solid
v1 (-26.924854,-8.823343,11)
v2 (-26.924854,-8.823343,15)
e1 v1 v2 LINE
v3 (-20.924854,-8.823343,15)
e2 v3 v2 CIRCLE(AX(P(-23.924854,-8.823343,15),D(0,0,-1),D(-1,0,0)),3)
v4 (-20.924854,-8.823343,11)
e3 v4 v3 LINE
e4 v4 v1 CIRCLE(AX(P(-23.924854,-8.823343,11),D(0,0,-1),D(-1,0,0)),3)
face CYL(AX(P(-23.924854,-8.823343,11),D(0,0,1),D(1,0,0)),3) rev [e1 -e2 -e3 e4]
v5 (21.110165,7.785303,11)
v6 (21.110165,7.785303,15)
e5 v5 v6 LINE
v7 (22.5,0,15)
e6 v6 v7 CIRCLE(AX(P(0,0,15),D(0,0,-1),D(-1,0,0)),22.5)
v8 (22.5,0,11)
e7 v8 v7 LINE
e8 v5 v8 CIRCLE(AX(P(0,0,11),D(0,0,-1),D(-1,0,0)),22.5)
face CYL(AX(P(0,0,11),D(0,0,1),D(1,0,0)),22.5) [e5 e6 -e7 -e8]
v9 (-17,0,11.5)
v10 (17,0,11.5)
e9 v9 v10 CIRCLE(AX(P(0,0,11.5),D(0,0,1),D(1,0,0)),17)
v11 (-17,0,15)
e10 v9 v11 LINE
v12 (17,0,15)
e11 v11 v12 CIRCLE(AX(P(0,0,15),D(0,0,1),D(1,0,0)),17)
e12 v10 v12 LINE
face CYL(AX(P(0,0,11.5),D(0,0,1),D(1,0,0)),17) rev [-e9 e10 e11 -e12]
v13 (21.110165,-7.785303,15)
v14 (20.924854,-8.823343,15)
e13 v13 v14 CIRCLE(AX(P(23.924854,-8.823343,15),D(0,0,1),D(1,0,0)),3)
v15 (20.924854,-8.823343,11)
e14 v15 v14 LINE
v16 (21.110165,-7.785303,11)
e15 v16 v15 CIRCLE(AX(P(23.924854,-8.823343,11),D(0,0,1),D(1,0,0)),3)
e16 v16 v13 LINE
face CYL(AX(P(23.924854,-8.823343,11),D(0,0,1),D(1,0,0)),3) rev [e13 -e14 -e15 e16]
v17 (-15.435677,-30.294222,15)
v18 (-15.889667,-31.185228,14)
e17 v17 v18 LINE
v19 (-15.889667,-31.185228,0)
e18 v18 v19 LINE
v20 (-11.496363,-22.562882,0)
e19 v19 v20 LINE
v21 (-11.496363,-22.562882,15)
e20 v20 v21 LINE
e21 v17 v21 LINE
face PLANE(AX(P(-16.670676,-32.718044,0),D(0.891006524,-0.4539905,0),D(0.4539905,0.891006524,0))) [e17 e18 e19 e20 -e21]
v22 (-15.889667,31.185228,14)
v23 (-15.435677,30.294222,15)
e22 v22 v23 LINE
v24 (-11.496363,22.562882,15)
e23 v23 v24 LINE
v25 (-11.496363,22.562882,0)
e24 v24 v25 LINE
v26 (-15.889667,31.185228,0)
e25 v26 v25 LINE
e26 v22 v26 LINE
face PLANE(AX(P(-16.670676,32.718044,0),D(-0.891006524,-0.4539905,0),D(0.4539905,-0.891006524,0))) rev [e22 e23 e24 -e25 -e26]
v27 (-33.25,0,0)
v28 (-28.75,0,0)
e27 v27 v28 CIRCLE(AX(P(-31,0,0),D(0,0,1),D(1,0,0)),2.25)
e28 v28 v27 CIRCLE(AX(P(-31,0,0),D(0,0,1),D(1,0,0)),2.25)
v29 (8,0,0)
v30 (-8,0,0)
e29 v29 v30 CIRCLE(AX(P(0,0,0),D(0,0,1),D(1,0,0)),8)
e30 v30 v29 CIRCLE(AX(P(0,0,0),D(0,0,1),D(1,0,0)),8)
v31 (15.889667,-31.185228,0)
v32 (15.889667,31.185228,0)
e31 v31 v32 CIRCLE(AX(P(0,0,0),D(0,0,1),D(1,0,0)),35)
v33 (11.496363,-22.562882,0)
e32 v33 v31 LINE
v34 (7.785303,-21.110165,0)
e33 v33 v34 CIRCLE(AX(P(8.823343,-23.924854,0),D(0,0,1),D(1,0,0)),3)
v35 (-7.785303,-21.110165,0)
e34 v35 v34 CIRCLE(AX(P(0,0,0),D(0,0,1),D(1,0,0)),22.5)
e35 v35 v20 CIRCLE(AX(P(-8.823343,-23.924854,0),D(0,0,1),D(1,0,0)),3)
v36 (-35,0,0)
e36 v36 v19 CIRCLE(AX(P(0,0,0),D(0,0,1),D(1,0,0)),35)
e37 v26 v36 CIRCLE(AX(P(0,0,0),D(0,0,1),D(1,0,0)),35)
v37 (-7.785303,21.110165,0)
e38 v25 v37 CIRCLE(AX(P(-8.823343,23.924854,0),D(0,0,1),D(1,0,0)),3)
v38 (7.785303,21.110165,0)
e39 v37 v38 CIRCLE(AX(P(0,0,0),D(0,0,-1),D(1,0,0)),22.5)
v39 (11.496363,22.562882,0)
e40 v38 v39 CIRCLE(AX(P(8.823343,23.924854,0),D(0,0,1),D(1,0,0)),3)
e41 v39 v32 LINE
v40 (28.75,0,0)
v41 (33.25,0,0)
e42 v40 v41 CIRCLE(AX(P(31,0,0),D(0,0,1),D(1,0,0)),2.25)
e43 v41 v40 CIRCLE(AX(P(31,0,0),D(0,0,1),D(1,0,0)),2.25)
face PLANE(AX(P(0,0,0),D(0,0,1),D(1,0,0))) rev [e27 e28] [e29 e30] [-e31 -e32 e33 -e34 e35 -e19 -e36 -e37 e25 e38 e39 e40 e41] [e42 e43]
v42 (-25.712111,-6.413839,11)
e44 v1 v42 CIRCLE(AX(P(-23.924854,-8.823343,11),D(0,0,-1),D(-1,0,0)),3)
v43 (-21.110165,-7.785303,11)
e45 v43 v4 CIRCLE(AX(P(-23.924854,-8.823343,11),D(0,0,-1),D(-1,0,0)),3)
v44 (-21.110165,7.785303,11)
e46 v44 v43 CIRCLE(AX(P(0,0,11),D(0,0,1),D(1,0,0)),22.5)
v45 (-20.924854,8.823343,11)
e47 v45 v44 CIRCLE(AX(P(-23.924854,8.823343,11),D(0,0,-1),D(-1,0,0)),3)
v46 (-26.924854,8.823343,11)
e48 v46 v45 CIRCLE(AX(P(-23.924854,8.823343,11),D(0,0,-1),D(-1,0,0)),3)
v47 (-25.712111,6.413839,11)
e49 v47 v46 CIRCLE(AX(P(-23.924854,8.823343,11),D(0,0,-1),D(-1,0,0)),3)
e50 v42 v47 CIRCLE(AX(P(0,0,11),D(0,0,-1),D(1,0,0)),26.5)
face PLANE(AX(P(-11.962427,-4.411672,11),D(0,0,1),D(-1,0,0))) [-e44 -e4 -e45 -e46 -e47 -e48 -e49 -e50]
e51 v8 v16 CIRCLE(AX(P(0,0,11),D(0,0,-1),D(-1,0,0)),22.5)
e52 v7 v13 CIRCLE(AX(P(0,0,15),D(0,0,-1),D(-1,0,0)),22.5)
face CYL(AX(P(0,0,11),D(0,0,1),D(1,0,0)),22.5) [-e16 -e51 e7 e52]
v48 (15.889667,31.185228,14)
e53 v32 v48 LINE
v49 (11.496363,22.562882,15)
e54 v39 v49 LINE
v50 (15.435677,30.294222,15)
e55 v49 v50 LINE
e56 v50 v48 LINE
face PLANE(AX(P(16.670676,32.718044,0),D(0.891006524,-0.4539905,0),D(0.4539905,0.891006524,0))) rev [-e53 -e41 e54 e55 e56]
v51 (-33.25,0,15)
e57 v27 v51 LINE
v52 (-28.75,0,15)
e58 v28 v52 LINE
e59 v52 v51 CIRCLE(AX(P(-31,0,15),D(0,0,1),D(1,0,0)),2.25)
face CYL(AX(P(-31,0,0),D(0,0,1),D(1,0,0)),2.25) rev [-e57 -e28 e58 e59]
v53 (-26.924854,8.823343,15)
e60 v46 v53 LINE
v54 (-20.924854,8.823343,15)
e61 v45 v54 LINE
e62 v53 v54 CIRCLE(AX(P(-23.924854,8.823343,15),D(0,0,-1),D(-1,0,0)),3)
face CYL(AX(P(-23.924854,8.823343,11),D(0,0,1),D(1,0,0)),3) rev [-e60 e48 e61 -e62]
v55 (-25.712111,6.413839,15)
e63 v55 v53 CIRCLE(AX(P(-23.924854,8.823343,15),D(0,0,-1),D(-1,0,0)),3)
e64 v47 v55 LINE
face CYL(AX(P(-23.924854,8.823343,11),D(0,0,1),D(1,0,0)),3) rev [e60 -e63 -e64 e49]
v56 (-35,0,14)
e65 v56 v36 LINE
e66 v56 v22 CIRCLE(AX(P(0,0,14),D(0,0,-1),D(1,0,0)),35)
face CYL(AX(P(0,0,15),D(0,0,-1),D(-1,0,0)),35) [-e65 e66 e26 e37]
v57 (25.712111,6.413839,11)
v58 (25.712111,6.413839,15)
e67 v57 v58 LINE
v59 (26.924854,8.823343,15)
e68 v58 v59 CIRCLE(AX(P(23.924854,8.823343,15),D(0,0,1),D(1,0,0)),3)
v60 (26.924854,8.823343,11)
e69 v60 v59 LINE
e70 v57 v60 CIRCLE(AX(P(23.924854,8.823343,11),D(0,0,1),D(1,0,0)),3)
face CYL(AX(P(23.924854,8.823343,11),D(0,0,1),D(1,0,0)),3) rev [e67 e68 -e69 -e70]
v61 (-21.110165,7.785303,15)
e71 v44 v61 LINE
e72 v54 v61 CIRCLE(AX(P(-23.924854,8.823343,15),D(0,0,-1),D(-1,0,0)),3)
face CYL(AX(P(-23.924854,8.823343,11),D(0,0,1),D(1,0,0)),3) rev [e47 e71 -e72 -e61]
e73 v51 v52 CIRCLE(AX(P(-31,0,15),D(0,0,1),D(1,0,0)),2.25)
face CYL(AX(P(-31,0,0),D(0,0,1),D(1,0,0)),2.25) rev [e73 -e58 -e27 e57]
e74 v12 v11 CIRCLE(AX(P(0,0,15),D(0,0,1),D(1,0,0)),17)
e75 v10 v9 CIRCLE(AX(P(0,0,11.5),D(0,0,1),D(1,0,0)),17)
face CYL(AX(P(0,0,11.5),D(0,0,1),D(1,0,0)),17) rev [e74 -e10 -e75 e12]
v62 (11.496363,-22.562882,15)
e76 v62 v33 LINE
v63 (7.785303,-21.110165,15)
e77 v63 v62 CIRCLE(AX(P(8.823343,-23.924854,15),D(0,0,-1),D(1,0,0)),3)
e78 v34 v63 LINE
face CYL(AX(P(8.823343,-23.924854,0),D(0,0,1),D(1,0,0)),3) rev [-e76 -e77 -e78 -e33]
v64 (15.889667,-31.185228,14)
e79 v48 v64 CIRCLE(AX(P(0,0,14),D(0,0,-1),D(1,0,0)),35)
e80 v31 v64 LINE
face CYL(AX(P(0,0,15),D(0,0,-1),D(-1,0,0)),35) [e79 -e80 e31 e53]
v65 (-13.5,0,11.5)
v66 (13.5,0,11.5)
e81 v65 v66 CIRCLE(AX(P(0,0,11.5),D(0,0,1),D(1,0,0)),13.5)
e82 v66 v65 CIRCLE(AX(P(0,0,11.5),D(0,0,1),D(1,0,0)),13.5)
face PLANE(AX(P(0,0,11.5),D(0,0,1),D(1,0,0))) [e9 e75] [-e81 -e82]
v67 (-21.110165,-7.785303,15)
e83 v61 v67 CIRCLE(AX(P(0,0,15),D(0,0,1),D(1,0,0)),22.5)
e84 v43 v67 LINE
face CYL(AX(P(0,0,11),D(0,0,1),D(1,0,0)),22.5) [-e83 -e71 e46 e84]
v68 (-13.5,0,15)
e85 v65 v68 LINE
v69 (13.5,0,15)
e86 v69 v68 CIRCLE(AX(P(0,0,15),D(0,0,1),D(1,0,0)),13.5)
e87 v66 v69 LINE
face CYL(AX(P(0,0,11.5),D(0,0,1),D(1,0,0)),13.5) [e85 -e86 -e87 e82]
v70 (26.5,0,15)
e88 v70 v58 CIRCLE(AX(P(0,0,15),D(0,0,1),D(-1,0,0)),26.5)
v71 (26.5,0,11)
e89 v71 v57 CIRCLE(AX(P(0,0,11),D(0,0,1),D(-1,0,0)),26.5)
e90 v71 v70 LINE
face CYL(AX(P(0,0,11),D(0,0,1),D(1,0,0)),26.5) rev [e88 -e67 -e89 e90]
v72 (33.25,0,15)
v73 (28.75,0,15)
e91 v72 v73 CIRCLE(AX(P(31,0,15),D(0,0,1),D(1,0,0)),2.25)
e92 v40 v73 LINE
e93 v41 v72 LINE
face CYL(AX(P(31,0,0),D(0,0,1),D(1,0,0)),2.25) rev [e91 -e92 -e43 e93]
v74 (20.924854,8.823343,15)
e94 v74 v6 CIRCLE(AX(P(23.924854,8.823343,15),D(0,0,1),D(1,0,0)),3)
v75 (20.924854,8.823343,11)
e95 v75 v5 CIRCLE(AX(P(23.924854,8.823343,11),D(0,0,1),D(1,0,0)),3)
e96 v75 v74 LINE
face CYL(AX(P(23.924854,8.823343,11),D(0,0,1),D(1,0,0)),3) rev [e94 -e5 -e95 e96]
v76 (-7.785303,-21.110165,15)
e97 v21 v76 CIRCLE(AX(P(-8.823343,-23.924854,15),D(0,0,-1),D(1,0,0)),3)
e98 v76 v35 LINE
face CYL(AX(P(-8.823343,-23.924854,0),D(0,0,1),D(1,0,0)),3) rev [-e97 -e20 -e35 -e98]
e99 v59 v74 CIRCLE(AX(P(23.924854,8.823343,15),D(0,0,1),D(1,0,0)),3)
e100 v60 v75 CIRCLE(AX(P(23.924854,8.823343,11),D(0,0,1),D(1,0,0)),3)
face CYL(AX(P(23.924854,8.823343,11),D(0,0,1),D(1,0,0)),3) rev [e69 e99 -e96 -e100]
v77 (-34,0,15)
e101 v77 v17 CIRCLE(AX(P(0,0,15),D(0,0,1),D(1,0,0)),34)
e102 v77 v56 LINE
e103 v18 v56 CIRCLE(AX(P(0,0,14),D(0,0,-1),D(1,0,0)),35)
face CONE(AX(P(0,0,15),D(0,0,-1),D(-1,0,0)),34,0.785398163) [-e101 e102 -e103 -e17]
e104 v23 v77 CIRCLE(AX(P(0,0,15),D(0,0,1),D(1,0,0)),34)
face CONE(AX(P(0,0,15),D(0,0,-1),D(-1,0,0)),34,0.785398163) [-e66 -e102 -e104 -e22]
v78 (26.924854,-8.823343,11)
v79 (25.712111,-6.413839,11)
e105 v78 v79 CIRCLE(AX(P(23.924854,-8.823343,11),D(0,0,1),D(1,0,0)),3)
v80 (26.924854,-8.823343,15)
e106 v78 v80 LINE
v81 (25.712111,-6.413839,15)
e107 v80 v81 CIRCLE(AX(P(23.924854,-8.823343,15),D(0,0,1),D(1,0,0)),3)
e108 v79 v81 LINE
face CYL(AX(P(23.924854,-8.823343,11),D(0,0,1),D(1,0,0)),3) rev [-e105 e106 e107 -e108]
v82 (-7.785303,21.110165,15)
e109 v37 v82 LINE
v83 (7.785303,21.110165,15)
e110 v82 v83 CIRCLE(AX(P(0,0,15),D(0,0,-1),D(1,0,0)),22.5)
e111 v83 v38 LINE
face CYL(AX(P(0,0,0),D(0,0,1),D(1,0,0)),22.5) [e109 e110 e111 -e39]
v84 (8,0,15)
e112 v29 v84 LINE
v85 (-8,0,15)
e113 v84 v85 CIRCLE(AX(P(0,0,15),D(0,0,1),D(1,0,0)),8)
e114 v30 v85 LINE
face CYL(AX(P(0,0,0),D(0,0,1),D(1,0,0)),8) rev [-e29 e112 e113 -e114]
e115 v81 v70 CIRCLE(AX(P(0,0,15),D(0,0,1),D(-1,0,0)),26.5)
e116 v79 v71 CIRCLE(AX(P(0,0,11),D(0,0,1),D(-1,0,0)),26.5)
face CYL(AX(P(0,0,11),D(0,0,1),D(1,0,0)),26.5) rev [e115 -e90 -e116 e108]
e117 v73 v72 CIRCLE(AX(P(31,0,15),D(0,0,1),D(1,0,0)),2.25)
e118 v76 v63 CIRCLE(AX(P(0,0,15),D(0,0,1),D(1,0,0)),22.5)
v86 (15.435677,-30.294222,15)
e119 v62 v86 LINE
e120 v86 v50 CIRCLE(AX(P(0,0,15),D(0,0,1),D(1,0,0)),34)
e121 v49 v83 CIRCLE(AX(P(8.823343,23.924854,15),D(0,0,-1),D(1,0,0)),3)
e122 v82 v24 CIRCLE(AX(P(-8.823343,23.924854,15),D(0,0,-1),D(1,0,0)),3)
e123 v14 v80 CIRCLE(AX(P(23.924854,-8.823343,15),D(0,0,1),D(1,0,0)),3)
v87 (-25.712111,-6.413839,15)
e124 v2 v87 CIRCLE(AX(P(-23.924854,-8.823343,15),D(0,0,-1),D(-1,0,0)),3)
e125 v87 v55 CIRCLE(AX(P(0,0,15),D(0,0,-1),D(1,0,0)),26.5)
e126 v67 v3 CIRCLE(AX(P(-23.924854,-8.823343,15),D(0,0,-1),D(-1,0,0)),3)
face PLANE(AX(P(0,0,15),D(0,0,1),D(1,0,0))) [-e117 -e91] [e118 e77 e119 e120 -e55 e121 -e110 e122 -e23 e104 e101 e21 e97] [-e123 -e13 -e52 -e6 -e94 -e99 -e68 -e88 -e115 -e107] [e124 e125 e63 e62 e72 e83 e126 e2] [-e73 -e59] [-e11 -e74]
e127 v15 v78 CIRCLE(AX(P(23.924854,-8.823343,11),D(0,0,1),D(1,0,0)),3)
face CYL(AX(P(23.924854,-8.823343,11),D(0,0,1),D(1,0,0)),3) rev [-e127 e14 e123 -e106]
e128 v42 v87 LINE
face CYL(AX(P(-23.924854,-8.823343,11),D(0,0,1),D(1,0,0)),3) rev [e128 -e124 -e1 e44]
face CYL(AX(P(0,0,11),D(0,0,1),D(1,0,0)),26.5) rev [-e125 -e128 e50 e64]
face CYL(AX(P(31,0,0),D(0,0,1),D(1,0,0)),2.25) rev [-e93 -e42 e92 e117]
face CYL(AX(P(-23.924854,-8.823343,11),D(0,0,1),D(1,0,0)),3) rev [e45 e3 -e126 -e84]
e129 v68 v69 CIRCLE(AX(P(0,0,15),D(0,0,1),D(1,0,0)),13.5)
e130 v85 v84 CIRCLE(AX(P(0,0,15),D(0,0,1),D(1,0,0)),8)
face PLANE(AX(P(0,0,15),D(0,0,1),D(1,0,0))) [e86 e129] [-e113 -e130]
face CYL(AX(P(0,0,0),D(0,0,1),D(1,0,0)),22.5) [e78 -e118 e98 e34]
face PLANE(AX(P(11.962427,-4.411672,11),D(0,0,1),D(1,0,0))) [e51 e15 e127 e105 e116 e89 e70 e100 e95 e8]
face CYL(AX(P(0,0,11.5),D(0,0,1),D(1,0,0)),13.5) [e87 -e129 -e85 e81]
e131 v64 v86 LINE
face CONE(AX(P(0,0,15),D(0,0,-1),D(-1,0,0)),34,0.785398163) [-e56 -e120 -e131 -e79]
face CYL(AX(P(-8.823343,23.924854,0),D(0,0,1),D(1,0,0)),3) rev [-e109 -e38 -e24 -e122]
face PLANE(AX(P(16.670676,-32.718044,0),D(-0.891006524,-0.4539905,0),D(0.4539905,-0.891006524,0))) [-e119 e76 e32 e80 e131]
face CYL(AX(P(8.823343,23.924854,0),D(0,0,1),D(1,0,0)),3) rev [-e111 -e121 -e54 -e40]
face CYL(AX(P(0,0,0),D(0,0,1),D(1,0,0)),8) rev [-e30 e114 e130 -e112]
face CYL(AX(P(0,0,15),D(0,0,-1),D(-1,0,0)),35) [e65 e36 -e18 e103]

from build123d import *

# Parameters (mm, degrees)
SKETCH_1_R             = 35
EXTRUDE_1_DEPTH        = 15
CUT_EXTRUDE_1_DEPTH    = 15
FILLET_1_R             = 3
FILLET_1_OF_MIRROR_1_R = 3
SKETCH_3_R             = 17
SKETCH_3_R_2           = 13.5
CUT_EXTRUDE_2_DEPTH    = 3.5
CUT_EXTRUDE_3_DEPTH    = 4
SKETCH_5_R             = 8
CUT_EXTRUDE_4_DEPTH    = 50.21908641
SKETCH_6_R             = 2.25
CUT_EXTRUDE_5_DEPTH    = 50.21908641
CHAMFER_1_SIZE         = 1


with BuildPart() as part:
    # 草图1 → 凸台-拉伸1 (new body)
    with BuildSketch(Plane.XY):
        Circle(SKETCH_1_R)
    extrude(amount=EXTRUDE_1_DEPTH)

    # 草图2 → 切除-拉伸1 (cut)
    with BuildSketch(Plane.XY.offset(15)):
        with BuildLine():
            Line((-16.670675913, 32.718043682), (-10.214786244, 20.047646794))
            ThreePointArc((-10.214786244, 20.047646794), (0, 22.5), (10.214786244, 20.047646794))
            Line((10.214786244, 20.047646794), (16.670675913, 32.718043682))
            ThreePointArc((16.670675913, 32.718043682), (0, 36.720318868), (-16.670675913, 32.718043682))
        make_face()
    cut_extrude_1 = extrude(amount=-CUT_EXTRUDE_1_DEPTH, mode=Mode.SUBTRACT)

    # 圆角1
    fillet_1_edges = [part.edges().sort_by_distance(p)[0] for p in [
        (-10.214786244, 20.047646794, 7.5),
        (10.214786244, 20.047646794, 7.5),
    ]]
    fillet(fillet_1_edges, radius=FILLET_1_R)

    # 镜向1: 切除-拉伸1 across plane
    add(cut_extrude_1.mirror(Plane.ZX), mode=Mode.SUBTRACT)

    # 圆角1 of 镜向1
    fillet_1_of_mirror_1_edges = [part.edges().sort_by_distance(p)[0] for p in [
        (-10.214786244, -20.047646794, 7.5),
        (10.214786244, -20.047646794, 7.5),
    ]]
    fillet(fillet_1_of_mirror_1_edges, radius=FILLET_1_OF_MIRROR_1_R)

    # 草图3 → 切除-拉伸2 (cut)
    with BuildSketch(Plane.XY.offset(15)):
        Circle(SKETCH_3_R)
        Circle(SKETCH_3_R_2, mode=Mode.SUBTRACT)
    extrude(amount=-CUT_EXTRUDE_2_DEPTH, mode=Mode.SUBTRACT)

    # 草图4 → 切除-拉伸3 (cut)
    with BuildSketch(Plane.XY.offset(15)):
        with BuildLine():
            ThreePointArc((21.110164899, 7.785302689), (22.5, 0), (21.110164899, -7.785302689))
            ThreePointArc((21.110164899, -7.785302689), (24.781668408, -11.69838536), (25.712111329, -6.413839024))
            ThreePointArc((25.712111329, -6.413839024), (26.5, 0), (25.712111329, 6.413839024))
            ThreePointArc((25.712111329, 6.413839024), (24.781668408, 11.69838536), (21.110164899, 7.785302689))
        make_face()
    cut_extrude_3 = extrude(amount=-CUT_EXTRUDE_3_DEPTH, mode=Mode.SUBTRACT)

    # 镜向2: 切除-拉伸3 across plane
    add(cut_extrude_3.mirror(Plane(origin=(0, 0, 0), x_dir=(0, 0, 1), z_dir=(1, 0, 0))), mode=Mode.SUBTRACT)

    # 草图5 → 切除-拉伸4 (cut, through all)
    with BuildSketch(Plane.XY.offset(15)):
        Circle(SKETCH_5_R)
    extrude(amount=-CUT_EXTRUDE_4_DEPTH, mode=Mode.SUBTRACT)

    # 草图6 → 切除-拉伸5 (cut, through all)
    with BuildSketch(Plane.XY.offset(15)):
        with Locations((-31, 0)):
            Circle(SKETCH_6_R)
        with Locations((31, 0)):
            Circle(SKETCH_6_R)
    extrude(amount=-CUT_EXTRUDE_5_DEPTH, mode=Mode.SUBTRACT)

    # 倒角1
    chamfer_1_edges = [part.edges().sort_by_distance(p)[0] for p in [
        (35, 0, 15),
        (-35, 0, 15),
    ]]
    chamfer(chamfer_1_edges, length=CHAMFER_1_SIZE)


solid = part.part
